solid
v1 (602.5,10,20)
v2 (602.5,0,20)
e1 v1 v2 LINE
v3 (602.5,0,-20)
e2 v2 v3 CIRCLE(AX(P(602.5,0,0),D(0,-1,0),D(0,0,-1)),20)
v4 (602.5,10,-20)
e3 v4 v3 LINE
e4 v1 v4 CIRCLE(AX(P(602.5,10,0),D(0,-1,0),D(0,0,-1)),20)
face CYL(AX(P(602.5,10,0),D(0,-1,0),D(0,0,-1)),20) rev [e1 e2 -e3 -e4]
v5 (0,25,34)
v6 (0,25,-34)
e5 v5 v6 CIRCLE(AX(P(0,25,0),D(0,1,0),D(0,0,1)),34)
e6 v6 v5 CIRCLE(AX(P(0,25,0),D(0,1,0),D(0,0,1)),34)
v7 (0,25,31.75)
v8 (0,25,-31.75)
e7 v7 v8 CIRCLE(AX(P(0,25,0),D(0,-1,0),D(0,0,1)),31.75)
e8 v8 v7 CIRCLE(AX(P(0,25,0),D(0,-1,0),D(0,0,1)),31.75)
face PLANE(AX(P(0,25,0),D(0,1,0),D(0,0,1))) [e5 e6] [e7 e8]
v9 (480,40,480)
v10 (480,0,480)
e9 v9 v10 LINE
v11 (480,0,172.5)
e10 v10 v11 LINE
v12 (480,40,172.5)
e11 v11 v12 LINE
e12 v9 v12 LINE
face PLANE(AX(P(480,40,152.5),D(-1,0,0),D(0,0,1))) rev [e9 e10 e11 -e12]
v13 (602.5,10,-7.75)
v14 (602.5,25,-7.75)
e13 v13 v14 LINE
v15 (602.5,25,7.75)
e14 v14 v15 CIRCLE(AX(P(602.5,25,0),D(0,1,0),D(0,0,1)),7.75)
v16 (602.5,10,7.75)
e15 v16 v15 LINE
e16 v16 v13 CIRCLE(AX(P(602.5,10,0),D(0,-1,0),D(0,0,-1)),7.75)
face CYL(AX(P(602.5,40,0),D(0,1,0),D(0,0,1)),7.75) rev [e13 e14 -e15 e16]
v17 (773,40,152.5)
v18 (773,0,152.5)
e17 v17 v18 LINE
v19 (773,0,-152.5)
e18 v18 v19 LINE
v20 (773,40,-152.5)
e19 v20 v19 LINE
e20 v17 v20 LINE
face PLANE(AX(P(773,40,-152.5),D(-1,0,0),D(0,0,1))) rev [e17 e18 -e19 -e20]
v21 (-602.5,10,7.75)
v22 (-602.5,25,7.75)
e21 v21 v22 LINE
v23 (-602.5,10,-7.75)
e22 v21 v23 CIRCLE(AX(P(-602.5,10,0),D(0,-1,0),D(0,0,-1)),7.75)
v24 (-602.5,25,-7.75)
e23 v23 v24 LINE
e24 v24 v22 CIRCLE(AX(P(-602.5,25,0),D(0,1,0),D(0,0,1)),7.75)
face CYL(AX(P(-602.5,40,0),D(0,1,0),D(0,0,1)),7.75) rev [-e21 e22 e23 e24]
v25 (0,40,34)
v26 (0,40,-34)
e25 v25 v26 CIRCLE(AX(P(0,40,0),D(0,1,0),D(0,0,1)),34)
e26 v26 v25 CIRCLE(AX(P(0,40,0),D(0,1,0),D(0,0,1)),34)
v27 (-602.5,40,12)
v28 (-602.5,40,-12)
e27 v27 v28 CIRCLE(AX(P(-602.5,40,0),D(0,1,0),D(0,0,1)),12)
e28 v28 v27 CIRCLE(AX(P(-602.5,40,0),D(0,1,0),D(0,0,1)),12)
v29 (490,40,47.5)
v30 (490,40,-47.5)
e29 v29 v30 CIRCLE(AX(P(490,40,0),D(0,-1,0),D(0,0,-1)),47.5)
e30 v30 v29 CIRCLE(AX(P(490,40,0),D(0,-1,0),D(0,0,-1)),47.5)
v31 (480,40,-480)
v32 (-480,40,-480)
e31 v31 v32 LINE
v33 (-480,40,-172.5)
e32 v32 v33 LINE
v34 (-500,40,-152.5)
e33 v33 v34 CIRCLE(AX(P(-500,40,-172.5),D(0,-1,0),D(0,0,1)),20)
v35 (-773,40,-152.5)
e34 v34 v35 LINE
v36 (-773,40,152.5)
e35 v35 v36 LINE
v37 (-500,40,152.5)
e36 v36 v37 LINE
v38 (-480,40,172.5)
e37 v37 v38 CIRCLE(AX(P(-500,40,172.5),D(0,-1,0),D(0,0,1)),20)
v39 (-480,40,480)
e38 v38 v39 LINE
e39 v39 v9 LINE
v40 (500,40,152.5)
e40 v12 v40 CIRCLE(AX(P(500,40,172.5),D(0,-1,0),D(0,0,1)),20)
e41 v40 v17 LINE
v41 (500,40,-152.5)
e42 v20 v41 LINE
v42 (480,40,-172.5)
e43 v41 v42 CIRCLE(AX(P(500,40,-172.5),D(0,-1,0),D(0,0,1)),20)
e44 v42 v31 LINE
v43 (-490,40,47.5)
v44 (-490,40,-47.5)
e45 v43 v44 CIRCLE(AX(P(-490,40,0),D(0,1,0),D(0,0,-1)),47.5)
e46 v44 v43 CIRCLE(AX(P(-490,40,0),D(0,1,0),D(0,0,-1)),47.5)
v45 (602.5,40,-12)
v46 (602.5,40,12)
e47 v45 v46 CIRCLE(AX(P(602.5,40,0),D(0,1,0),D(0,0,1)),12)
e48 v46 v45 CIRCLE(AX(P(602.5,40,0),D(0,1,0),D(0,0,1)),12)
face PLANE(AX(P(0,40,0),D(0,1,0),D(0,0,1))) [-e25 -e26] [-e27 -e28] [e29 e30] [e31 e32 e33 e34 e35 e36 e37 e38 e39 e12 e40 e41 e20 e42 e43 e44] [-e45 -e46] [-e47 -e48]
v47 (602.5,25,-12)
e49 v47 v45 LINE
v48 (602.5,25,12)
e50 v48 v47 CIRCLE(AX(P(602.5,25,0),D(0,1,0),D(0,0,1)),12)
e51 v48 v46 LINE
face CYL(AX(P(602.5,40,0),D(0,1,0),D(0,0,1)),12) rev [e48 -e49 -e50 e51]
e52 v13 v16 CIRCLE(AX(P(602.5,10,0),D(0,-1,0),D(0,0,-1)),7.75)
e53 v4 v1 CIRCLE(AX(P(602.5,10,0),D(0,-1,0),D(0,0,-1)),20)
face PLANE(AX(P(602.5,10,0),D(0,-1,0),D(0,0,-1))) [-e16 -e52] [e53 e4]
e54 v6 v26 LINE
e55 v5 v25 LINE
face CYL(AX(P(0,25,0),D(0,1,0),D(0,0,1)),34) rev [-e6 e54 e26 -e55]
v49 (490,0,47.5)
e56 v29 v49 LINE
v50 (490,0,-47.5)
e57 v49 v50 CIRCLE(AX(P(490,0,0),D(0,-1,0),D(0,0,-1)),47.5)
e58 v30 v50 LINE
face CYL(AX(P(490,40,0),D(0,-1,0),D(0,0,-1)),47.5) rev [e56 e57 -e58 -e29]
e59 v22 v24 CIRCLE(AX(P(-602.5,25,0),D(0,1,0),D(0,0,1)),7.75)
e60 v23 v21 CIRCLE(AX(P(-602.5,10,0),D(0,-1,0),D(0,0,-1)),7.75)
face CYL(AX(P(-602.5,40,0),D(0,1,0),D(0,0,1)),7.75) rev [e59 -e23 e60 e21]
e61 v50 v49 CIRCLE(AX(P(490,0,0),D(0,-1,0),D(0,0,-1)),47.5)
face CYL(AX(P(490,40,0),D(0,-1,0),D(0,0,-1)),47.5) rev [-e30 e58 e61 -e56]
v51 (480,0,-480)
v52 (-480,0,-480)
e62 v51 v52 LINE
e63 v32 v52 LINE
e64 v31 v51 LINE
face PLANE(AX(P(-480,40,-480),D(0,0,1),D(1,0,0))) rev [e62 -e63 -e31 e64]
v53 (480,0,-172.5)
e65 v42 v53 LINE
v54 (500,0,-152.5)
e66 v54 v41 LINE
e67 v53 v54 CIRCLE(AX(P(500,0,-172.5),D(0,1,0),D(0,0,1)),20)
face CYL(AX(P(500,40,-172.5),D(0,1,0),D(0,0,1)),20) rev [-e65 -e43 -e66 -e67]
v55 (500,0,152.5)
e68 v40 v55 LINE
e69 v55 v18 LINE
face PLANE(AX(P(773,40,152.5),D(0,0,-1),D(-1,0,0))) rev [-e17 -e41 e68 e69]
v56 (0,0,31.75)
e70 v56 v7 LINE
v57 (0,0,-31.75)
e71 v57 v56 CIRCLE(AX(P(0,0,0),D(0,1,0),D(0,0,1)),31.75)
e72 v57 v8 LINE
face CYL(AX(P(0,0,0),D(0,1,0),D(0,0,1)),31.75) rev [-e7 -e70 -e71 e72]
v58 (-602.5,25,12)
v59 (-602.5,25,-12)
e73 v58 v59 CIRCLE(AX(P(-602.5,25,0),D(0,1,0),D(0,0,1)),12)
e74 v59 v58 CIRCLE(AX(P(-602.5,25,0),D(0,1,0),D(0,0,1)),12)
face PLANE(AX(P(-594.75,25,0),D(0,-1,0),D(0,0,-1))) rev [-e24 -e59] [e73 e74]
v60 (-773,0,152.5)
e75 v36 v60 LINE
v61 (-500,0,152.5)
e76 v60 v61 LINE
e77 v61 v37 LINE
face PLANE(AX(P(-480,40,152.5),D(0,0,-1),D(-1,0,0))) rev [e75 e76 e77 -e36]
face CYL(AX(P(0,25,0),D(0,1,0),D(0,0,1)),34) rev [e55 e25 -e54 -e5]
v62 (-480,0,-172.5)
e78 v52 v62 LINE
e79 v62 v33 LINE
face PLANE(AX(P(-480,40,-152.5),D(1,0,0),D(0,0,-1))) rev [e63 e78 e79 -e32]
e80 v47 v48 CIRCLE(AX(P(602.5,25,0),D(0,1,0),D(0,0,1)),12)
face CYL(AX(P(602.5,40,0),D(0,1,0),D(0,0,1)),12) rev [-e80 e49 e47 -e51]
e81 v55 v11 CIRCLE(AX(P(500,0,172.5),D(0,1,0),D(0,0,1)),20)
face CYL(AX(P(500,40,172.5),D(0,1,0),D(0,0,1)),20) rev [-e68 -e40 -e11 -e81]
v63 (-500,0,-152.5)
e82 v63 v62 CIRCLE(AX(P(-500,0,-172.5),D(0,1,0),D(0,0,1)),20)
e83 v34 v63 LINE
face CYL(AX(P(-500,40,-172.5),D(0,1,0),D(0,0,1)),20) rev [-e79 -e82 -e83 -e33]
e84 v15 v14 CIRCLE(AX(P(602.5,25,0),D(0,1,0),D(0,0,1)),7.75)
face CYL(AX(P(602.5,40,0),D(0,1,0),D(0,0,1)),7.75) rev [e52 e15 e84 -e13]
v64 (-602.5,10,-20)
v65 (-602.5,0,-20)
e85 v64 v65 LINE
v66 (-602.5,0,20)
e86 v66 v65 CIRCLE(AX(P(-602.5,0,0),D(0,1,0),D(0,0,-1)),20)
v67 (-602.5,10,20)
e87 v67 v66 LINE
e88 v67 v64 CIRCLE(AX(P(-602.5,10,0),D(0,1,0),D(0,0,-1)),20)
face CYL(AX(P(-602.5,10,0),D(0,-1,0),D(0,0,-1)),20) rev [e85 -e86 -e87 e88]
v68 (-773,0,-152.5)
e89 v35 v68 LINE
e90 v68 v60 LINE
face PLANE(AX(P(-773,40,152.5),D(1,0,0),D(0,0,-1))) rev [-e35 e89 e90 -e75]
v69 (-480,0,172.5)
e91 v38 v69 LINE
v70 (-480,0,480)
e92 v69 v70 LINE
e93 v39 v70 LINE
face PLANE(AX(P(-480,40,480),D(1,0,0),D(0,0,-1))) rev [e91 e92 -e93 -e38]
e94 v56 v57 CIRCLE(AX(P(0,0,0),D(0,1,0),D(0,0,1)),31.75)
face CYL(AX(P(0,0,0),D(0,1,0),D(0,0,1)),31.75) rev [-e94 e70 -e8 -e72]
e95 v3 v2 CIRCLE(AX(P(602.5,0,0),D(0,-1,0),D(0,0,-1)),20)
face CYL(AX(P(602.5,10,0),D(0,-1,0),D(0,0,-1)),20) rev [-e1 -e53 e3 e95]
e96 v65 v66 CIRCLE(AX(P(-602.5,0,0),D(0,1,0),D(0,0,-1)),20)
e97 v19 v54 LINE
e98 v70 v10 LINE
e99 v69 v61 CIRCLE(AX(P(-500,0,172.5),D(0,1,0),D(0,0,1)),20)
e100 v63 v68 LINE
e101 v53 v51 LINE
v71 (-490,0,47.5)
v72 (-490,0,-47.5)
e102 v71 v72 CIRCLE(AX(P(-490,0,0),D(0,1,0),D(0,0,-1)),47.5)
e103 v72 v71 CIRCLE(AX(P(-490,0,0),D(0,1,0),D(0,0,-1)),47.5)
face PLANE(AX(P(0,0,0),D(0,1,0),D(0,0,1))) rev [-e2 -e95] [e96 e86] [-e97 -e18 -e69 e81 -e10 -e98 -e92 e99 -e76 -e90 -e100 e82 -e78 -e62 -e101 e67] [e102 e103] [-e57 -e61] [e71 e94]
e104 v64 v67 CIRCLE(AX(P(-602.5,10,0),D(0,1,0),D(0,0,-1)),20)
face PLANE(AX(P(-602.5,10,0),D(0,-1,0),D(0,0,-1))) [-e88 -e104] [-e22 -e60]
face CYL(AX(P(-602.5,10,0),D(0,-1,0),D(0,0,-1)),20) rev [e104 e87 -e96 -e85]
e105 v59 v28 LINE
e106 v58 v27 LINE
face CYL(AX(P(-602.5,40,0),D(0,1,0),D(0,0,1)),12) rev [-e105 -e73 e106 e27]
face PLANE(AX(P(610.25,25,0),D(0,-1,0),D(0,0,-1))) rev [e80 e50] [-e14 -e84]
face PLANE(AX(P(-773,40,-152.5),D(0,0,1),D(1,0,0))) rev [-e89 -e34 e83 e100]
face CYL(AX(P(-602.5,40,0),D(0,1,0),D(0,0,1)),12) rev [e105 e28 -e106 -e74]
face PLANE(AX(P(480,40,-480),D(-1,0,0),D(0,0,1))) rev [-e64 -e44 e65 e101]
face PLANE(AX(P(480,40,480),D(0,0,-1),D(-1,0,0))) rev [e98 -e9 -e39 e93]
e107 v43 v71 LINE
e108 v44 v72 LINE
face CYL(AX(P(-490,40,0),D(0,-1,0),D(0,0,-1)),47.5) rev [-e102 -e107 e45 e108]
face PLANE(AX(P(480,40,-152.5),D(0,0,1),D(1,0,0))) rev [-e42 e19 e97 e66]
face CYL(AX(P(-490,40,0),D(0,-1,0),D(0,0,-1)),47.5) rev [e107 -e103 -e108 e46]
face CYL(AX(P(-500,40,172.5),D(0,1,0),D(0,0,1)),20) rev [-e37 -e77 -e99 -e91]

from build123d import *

# Parameters (mm, degrees)
EXTRUDE_1_DEPTH           = 40
SKETCH_2_R                = 20
CUT_EXTRUDE_1_DEPTH       = 10
HOLE_WIZARD_0_D           = 15.5
HOLE_WIZARD_0_CBORE_D     = 24
HOLE_WIZARD_0_CBORE_DEPTH = 15
SKETCH_5_R                = 47.5
CUT_EXTRUDE_2_DEPTH       = 911.7848264
SKETCH_6_R                = 31.75
CUT_EXTRUDE_3_DEPTH       = 911.7848264
FILLET_1_R                = 20
SKETCH_7_R                = 34
CUT_EXTRUDE_4_DEPTH       = 15


with BuildPart() as part:
    # 草图1 → 凸台-拉伸1 (new body)
    with BuildSketch(Plane(origin=(0, 0, 0), x_dir=(1, 0, 0), z_dir=(0, 1, 0))):
        Polygon((-480, 480), (480, 480), (480, 152.5), (773, 152.5), (773, -152.5), (480, -152.5), (480, -480), (-480, -480), (-480, -152.5), (-773, -152.5), (-773, 152.5), (-480, 152.5), align=None)
    extrude(amount=EXTRUDE_1_DEPTH)

    # 草图2 → 切除-拉伸1 (cut)
    with BuildSketch(Plane.XZ):
        with Locations(Location((602.5, 0, 0), (0, 0, 270))):
            Circle(SKETCH_2_R)
    cut_extrude_1 = extrude(amount=-CUT_EXTRUDE_1_DEPTH, mode=Mode.SUBTRACT)

    # 打孔尺寸(%根据)内六角圆柱头螺钉的类型0 (through all)
    with Locations(Plane(origin=(0, 40, 0), x_dir=(1, 0, 0), z_dir=(0, 1, 0))):
        with Locations((602.5, 0)):
            hole_wizard_0 = CounterBoreHole(HOLE_WIZARD_0_D / 2, HOLE_WIZARD_0_CBORE_D / 2, HOLE_WIZARD_0_CBORE_DEPTH)

    # 镜向1: 切除-拉伸1, 打孔尺寸(%根据)内六角圆柱头螺钉的类型0 across plane
    add(cut_extrude_1.mirror(Plane(origin=(0, 0, 0), x_dir=(0, 0, 1), z_dir=(1, 0, 0))), mode=Mode.SUBTRACT)
    add(hole_wizard_0.mirror(Plane(origin=(0, 0, 0), x_dir=(0, 0, 1), z_dir=(1, 0, 0))), mode=Mode.SUBTRACT)

    # 草图5 → 切除-拉伸2 (cut, through all)
    with BuildSketch(Plane.XZ):
        with Locations(Location((490, 0, 0), (0, 0, 270))):
            Circle(SKETCH_5_R)
    cut_extrude_2 = extrude(amount=-CUT_EXTRUDE_2_DEPTH, mode=Mode.SUBTRACT)

    # 镜向2: 切除-拉伸2 across plane
    add(cut_extrude_2.mirror(Plane(origin=(0, 0, 0), x_dir=(0, 0, 1), z_dir=(1, 0, 0))), mode=Mode.SUBTRACT)

    # 草图6 → 切除-拉伸3 (cut, through all)
    with BuildSketch(Plane(origin=(0, 40, 0), x_dir=(1, 0, 0), z_dir=(0, 1, 0))):
        with Locations(Location((0, 0, 0), (0, 0, 270))):
            Circle(SKETCH_6_R)
    extrude(amount=-CUT_EXTRUDE_3_DEPTH, mode=Mode.SUBTRACT)

    # 圆角1
    fillet_1_edges = [part.edges().sort_by_distance(p)[0] for p in [
        (-480, 20, 152.5),
        (-480, 20, -152.5),
        (480, 20, -152.5),
        (480, 20, 152.5),
    ]]
    fillet(fillet_1_edges, radius=FILLET_1_R)

    # 草图7 → 切除-拉伸4 (cut)
    with BuildSketch(Plane(origin=(0, 40, 0), x_dir=(1, 0, 0), z_dir=(0, 1, 0))):
        with Locations(Location((0, 0, 0), (0, 0, 270))):
            Circle(SKETCH_7_R)
    extrude(amount=-CUT_EXTRUDE_4_DEPTH, mode=Mode.SUBTRACT)


solid = part.part
